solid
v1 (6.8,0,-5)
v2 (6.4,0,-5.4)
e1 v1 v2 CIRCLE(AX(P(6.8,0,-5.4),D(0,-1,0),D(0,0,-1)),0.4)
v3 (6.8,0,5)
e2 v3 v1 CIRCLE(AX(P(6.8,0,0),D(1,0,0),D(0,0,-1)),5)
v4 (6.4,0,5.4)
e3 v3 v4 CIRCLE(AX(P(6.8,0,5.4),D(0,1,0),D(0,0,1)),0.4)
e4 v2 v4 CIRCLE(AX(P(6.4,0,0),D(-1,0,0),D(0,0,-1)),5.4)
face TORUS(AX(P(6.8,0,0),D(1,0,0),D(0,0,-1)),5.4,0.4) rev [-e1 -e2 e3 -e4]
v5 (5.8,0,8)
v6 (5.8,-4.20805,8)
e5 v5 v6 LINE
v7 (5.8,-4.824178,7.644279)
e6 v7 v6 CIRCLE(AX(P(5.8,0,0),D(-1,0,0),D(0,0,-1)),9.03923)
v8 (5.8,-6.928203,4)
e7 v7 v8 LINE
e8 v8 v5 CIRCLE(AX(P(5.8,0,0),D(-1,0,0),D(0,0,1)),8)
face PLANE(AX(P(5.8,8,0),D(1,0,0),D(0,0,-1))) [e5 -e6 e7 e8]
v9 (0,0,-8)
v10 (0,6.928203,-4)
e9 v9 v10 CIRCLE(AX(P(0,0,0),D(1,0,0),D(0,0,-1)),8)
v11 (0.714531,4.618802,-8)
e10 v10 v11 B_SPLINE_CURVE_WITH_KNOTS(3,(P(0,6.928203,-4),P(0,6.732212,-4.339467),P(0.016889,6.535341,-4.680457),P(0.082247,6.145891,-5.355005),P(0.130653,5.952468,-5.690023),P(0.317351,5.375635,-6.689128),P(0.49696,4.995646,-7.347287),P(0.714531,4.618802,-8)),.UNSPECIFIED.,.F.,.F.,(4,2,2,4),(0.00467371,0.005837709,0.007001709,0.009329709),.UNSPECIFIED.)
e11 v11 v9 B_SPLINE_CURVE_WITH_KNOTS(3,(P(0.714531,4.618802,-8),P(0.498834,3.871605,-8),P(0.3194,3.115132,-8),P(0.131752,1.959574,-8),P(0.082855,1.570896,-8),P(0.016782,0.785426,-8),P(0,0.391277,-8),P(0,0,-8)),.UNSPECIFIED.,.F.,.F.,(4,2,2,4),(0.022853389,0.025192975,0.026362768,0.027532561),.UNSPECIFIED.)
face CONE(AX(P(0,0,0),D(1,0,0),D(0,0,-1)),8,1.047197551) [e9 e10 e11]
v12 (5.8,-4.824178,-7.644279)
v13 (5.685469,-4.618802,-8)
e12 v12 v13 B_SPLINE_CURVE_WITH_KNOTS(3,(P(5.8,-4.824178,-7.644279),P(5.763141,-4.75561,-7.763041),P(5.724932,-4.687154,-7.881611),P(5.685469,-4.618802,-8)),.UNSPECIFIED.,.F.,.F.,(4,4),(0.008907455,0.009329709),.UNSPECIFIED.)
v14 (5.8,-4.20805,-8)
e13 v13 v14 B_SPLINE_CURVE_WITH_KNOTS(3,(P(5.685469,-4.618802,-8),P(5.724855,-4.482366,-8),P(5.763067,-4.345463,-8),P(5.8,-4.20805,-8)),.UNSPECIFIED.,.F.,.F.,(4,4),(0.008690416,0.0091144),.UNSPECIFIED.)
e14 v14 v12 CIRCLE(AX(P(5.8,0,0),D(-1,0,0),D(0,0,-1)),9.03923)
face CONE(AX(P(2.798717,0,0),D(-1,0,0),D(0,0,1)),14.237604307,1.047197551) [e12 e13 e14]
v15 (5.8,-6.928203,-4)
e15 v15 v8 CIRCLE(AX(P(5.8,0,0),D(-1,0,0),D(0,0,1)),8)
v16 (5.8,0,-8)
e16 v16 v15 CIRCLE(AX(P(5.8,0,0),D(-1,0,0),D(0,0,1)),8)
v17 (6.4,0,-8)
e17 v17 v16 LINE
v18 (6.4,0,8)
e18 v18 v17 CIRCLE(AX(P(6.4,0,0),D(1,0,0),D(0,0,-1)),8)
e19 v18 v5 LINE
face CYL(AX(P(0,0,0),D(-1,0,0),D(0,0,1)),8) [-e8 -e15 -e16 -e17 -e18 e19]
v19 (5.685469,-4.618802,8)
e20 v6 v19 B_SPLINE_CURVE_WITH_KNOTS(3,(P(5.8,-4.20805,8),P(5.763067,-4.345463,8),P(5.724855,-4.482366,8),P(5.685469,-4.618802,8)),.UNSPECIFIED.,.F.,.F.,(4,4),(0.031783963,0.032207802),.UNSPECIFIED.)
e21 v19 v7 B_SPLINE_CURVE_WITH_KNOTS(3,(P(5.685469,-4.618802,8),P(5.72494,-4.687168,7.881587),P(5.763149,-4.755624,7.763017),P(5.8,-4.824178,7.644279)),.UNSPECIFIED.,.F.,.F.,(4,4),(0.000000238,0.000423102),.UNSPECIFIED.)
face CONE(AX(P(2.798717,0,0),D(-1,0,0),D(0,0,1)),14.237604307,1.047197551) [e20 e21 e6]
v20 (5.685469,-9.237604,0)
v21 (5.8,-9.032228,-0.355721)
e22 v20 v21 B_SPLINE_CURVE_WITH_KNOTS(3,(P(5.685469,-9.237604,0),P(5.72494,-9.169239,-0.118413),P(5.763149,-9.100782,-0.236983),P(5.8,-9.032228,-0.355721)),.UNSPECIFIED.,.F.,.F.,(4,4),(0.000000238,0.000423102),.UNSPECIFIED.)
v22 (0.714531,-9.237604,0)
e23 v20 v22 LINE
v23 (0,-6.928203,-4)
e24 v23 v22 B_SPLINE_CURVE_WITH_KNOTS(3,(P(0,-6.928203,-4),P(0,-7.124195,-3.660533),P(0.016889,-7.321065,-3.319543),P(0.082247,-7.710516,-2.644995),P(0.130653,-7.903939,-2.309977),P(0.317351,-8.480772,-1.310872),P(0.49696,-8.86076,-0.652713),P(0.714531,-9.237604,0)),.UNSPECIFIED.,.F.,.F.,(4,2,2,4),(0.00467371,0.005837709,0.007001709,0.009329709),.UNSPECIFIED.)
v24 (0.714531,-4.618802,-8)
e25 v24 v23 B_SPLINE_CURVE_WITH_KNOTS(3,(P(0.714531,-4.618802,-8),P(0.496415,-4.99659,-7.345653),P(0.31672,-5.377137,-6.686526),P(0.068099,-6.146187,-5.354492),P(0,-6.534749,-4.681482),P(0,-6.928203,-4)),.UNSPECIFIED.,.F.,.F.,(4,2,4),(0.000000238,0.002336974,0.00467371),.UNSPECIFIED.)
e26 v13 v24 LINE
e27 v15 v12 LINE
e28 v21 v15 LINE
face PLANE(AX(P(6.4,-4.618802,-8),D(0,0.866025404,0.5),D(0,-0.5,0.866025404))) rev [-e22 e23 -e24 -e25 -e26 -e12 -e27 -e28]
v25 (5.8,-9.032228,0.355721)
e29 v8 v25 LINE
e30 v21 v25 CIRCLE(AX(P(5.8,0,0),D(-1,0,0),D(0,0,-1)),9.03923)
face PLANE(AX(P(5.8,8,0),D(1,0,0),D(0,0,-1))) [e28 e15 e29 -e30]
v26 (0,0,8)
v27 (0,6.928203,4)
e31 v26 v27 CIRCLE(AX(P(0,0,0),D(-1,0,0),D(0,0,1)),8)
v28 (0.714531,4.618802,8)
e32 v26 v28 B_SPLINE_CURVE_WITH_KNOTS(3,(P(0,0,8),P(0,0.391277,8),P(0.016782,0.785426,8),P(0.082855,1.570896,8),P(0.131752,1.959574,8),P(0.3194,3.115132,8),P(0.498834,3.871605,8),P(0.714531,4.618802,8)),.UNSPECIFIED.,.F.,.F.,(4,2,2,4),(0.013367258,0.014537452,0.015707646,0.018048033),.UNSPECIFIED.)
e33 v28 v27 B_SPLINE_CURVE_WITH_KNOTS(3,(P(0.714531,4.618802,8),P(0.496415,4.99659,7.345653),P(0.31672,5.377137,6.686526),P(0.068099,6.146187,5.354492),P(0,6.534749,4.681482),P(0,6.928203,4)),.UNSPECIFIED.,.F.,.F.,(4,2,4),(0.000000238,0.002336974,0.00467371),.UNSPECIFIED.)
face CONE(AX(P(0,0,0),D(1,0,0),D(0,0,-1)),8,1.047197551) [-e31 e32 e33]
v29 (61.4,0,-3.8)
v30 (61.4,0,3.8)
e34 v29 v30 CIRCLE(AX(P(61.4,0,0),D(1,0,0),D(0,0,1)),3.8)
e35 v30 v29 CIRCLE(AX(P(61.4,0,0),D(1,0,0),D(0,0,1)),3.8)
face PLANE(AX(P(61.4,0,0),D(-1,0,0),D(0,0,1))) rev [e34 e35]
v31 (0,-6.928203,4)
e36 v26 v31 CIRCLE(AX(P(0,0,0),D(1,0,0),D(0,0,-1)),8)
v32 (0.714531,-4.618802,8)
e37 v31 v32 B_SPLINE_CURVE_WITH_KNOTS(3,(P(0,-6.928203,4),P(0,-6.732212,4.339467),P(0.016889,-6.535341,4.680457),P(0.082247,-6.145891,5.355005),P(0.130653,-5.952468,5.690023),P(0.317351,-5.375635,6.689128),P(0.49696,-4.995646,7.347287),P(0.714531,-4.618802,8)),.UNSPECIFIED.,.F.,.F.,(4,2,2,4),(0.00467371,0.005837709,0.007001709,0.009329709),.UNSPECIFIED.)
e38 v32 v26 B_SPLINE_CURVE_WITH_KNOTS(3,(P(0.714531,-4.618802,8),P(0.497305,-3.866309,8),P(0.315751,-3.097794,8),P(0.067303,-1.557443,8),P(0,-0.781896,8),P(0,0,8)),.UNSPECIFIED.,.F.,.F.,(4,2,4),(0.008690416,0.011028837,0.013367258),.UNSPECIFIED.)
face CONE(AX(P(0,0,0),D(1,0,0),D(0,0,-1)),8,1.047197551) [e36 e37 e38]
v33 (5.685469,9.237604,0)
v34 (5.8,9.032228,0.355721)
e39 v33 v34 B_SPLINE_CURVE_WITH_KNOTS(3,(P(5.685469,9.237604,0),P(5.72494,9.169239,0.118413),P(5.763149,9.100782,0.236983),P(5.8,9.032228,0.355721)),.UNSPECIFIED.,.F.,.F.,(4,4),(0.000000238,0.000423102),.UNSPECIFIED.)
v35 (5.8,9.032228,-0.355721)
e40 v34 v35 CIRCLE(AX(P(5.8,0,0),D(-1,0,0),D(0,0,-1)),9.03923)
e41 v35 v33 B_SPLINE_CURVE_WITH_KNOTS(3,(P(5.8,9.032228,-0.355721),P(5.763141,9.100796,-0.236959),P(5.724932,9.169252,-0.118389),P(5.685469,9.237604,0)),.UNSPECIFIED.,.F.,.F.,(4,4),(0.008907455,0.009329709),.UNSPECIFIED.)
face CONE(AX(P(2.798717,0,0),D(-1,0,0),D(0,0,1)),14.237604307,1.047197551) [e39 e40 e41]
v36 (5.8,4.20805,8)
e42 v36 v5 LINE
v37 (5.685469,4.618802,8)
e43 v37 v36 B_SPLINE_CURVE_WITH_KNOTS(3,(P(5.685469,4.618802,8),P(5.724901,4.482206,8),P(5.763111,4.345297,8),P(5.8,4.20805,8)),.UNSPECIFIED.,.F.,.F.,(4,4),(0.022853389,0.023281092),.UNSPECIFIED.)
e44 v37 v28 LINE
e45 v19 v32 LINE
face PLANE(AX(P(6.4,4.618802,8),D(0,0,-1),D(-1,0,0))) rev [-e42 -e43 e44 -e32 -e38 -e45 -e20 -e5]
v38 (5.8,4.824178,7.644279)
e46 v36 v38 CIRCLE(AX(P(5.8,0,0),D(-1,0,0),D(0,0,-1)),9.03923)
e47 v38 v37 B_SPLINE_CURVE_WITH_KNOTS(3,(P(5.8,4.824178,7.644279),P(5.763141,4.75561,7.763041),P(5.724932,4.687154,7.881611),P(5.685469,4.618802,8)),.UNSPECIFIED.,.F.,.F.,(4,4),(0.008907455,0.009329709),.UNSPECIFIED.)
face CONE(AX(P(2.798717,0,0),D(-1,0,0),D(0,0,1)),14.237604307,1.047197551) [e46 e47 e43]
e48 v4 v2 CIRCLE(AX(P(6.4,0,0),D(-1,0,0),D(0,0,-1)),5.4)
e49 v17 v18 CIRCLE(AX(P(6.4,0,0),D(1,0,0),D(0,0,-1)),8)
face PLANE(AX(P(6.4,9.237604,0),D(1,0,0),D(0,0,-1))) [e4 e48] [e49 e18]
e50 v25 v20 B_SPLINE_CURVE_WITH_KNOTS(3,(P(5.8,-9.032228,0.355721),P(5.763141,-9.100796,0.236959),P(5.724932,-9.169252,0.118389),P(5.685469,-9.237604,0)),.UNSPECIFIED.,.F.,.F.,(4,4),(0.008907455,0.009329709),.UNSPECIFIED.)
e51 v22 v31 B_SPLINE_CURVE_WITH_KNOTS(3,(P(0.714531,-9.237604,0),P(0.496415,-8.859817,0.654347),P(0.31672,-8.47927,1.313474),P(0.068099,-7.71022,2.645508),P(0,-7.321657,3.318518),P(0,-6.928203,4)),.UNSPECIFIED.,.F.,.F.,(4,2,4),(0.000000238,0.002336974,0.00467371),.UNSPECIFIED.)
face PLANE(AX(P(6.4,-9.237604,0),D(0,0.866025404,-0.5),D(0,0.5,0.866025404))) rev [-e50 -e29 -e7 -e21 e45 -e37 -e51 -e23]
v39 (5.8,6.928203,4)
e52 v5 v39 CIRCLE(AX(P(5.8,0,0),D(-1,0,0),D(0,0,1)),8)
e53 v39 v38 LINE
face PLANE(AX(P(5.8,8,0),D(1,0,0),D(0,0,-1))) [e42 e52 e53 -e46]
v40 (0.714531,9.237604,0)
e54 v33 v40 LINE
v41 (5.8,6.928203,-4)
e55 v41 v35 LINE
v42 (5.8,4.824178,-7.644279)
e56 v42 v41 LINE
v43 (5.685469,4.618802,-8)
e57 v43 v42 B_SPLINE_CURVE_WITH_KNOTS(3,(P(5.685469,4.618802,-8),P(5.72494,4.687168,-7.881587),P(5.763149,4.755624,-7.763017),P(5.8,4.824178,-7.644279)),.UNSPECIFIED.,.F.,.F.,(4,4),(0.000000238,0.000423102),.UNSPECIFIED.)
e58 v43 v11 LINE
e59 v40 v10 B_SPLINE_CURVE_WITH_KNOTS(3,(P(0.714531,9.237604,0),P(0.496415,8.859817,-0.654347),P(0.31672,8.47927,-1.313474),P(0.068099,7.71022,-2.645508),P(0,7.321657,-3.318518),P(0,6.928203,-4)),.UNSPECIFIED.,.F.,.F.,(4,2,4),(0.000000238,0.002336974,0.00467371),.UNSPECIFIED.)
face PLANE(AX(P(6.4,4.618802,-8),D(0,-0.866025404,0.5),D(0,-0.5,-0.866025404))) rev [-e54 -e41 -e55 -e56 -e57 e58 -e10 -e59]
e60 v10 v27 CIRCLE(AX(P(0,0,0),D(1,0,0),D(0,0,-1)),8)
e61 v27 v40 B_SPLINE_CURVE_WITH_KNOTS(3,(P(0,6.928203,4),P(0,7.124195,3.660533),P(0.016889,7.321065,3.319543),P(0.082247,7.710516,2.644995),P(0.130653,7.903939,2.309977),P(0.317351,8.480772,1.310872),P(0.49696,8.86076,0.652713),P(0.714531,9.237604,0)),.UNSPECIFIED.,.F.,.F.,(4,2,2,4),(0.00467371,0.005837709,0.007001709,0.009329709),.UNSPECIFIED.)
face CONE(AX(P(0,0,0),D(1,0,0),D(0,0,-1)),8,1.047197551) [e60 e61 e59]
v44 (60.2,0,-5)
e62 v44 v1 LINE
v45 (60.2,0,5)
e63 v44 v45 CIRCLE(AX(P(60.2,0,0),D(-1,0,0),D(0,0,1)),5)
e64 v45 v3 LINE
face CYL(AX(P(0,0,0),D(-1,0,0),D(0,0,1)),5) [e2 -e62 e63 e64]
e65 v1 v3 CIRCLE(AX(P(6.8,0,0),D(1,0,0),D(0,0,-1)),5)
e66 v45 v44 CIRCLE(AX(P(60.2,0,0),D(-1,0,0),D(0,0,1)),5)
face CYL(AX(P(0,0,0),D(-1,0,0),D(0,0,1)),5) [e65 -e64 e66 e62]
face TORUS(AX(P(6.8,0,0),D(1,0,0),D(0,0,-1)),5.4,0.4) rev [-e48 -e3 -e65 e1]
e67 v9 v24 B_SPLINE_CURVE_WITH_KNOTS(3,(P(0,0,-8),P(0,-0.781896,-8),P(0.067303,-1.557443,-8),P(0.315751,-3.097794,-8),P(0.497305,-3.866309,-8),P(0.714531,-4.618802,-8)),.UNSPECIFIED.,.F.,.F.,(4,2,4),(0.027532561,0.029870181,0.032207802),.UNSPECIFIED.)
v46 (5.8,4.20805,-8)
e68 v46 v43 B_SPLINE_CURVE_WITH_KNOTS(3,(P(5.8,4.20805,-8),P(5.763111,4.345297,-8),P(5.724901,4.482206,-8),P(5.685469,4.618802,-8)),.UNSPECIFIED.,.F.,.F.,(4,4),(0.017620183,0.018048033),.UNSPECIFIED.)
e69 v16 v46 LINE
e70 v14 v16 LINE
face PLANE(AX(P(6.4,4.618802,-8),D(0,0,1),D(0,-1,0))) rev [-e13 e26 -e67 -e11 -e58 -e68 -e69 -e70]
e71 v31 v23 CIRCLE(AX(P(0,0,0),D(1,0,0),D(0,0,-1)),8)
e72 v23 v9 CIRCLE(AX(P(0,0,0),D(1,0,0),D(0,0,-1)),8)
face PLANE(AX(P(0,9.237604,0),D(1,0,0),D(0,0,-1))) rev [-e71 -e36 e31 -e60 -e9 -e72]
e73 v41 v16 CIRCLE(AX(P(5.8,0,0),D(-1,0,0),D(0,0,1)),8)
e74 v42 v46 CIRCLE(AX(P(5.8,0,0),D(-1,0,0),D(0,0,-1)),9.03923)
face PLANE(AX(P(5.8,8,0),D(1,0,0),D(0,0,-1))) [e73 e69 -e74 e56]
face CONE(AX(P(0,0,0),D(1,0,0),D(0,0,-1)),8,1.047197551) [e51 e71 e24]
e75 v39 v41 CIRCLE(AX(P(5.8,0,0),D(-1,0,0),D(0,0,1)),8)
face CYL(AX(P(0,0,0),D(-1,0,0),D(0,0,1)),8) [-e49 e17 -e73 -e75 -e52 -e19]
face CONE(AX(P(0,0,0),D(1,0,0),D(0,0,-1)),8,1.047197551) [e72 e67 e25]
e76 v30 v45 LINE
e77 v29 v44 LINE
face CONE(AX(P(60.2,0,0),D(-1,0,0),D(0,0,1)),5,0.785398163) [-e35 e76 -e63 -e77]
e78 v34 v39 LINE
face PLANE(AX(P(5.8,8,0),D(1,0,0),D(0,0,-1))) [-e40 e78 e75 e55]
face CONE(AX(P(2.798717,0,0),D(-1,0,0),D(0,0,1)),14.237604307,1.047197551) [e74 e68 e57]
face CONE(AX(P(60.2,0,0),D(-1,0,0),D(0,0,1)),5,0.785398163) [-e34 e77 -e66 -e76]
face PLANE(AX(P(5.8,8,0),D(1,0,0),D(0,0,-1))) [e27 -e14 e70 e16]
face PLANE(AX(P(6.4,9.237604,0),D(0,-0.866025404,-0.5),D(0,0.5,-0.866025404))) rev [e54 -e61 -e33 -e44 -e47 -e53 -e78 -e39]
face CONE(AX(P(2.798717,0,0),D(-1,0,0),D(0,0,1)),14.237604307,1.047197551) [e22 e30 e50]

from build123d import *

# Parameters (mm, degrees)
EXTRUDE_371_DEPTH = 6.4
SKETCH_4_W        = 0.6
SKETCH_4_H        = 11.237604307
CHAMFER_2038_SIZE = 1.2
FILLET_2080_R     = 0.4


with BuildPart() as part:
    # 草图1 → Extrude 371 (new body)
    with BuildSketch(Plane(origin=(0, 0, 0), x_dir=(0, 0, -1), z_dir=(1, 0, 0))):
        Polygon((8, 4.618802154), (8, -4.618802154), (0, -9.237604307), (-8, -4.618802154), (-8, 4.618802154), (0, 9.237604307), align=None)
    extrude(amount=EXTRUDE_371_DEPTH)

    # 草图2 → 凸台-旋转1 (revolve)
    with BuildSketch(Plane.XY, mode=Mode.PRIVATE) as revolve_1_sk:
        Polygon((0, 0), (61.4, 0), (61.4, 3.701), (61.4, 5), (27.8072, 5), (0, 5), align=None)
    revolve(revolve_1_sk.sketch.rotate(Axis((0, 0, 0), (1, 0, 0)), 90), axis=Axis((0, 0, 0), (1, 0, 0)))

    # 草图3 → 切除-旋转1 (revolve, cut)
    with BuildSketch(Plane.XY):
        Polygon((0, 8), (3.601282526, 14.237604307), (3.601282526, 19.237604307), (-10, 19.237604307), (-10, 8), align=None)
    revolve(axis=Axis((0, 0, 0), (1, 0, 0)), mode=Mode.SUBTRACT)

    # 草图5 → 切除-旋转2 (revolve, cut)
    with BuildSketch(Plane.XY):
        Polygon((6.4, 8), (2.798717474, 14.237604307), (2.798717474, 19.237604307), (12.798717474, 19.237604307), (12.798717474, 8), align=None)
    revolve(axis=Axis((0, 0, 0), (1, 0, 0)), mode=Mode.SUBTRACT)

    # 草图4 → 切除-旋转3 (revolve, cut)
    with BuildSketch(Plane.XY, mode=Mode.PRIVATE) as cut_revolve_3_sk:
        with Locations((6.1, 13.618802154)):
            Rectangle(SKETCH_4_W, SKETCH_4_H)
    revolve(cut_revolve_3_sk.sketch.rotate(Axis((0, 0, 0), (1, 0, 0)), 270), axis=Axis((0, 0, 0), (1, 0, 0)), mode=Mode.SUBTRACT)

    # Chamfer 2038
    chamfer_2038_edges = [part.edges().sort_by_distance(p)[0] for p in [
        (61.4, 0, -5),
    ]]
    chamfer(chamfer_2038_edges, length=CHAMFER_2038_SIZE)

    # Fillet 2080
    fillet_2080_edges = [part.edges().sort_by_distance(p)[0] for p in [
        (6.4, 0, -5),
    ]]
    fillet(fillet_2080_edges, radius=FILLET_2080_R)


solid = part.part
